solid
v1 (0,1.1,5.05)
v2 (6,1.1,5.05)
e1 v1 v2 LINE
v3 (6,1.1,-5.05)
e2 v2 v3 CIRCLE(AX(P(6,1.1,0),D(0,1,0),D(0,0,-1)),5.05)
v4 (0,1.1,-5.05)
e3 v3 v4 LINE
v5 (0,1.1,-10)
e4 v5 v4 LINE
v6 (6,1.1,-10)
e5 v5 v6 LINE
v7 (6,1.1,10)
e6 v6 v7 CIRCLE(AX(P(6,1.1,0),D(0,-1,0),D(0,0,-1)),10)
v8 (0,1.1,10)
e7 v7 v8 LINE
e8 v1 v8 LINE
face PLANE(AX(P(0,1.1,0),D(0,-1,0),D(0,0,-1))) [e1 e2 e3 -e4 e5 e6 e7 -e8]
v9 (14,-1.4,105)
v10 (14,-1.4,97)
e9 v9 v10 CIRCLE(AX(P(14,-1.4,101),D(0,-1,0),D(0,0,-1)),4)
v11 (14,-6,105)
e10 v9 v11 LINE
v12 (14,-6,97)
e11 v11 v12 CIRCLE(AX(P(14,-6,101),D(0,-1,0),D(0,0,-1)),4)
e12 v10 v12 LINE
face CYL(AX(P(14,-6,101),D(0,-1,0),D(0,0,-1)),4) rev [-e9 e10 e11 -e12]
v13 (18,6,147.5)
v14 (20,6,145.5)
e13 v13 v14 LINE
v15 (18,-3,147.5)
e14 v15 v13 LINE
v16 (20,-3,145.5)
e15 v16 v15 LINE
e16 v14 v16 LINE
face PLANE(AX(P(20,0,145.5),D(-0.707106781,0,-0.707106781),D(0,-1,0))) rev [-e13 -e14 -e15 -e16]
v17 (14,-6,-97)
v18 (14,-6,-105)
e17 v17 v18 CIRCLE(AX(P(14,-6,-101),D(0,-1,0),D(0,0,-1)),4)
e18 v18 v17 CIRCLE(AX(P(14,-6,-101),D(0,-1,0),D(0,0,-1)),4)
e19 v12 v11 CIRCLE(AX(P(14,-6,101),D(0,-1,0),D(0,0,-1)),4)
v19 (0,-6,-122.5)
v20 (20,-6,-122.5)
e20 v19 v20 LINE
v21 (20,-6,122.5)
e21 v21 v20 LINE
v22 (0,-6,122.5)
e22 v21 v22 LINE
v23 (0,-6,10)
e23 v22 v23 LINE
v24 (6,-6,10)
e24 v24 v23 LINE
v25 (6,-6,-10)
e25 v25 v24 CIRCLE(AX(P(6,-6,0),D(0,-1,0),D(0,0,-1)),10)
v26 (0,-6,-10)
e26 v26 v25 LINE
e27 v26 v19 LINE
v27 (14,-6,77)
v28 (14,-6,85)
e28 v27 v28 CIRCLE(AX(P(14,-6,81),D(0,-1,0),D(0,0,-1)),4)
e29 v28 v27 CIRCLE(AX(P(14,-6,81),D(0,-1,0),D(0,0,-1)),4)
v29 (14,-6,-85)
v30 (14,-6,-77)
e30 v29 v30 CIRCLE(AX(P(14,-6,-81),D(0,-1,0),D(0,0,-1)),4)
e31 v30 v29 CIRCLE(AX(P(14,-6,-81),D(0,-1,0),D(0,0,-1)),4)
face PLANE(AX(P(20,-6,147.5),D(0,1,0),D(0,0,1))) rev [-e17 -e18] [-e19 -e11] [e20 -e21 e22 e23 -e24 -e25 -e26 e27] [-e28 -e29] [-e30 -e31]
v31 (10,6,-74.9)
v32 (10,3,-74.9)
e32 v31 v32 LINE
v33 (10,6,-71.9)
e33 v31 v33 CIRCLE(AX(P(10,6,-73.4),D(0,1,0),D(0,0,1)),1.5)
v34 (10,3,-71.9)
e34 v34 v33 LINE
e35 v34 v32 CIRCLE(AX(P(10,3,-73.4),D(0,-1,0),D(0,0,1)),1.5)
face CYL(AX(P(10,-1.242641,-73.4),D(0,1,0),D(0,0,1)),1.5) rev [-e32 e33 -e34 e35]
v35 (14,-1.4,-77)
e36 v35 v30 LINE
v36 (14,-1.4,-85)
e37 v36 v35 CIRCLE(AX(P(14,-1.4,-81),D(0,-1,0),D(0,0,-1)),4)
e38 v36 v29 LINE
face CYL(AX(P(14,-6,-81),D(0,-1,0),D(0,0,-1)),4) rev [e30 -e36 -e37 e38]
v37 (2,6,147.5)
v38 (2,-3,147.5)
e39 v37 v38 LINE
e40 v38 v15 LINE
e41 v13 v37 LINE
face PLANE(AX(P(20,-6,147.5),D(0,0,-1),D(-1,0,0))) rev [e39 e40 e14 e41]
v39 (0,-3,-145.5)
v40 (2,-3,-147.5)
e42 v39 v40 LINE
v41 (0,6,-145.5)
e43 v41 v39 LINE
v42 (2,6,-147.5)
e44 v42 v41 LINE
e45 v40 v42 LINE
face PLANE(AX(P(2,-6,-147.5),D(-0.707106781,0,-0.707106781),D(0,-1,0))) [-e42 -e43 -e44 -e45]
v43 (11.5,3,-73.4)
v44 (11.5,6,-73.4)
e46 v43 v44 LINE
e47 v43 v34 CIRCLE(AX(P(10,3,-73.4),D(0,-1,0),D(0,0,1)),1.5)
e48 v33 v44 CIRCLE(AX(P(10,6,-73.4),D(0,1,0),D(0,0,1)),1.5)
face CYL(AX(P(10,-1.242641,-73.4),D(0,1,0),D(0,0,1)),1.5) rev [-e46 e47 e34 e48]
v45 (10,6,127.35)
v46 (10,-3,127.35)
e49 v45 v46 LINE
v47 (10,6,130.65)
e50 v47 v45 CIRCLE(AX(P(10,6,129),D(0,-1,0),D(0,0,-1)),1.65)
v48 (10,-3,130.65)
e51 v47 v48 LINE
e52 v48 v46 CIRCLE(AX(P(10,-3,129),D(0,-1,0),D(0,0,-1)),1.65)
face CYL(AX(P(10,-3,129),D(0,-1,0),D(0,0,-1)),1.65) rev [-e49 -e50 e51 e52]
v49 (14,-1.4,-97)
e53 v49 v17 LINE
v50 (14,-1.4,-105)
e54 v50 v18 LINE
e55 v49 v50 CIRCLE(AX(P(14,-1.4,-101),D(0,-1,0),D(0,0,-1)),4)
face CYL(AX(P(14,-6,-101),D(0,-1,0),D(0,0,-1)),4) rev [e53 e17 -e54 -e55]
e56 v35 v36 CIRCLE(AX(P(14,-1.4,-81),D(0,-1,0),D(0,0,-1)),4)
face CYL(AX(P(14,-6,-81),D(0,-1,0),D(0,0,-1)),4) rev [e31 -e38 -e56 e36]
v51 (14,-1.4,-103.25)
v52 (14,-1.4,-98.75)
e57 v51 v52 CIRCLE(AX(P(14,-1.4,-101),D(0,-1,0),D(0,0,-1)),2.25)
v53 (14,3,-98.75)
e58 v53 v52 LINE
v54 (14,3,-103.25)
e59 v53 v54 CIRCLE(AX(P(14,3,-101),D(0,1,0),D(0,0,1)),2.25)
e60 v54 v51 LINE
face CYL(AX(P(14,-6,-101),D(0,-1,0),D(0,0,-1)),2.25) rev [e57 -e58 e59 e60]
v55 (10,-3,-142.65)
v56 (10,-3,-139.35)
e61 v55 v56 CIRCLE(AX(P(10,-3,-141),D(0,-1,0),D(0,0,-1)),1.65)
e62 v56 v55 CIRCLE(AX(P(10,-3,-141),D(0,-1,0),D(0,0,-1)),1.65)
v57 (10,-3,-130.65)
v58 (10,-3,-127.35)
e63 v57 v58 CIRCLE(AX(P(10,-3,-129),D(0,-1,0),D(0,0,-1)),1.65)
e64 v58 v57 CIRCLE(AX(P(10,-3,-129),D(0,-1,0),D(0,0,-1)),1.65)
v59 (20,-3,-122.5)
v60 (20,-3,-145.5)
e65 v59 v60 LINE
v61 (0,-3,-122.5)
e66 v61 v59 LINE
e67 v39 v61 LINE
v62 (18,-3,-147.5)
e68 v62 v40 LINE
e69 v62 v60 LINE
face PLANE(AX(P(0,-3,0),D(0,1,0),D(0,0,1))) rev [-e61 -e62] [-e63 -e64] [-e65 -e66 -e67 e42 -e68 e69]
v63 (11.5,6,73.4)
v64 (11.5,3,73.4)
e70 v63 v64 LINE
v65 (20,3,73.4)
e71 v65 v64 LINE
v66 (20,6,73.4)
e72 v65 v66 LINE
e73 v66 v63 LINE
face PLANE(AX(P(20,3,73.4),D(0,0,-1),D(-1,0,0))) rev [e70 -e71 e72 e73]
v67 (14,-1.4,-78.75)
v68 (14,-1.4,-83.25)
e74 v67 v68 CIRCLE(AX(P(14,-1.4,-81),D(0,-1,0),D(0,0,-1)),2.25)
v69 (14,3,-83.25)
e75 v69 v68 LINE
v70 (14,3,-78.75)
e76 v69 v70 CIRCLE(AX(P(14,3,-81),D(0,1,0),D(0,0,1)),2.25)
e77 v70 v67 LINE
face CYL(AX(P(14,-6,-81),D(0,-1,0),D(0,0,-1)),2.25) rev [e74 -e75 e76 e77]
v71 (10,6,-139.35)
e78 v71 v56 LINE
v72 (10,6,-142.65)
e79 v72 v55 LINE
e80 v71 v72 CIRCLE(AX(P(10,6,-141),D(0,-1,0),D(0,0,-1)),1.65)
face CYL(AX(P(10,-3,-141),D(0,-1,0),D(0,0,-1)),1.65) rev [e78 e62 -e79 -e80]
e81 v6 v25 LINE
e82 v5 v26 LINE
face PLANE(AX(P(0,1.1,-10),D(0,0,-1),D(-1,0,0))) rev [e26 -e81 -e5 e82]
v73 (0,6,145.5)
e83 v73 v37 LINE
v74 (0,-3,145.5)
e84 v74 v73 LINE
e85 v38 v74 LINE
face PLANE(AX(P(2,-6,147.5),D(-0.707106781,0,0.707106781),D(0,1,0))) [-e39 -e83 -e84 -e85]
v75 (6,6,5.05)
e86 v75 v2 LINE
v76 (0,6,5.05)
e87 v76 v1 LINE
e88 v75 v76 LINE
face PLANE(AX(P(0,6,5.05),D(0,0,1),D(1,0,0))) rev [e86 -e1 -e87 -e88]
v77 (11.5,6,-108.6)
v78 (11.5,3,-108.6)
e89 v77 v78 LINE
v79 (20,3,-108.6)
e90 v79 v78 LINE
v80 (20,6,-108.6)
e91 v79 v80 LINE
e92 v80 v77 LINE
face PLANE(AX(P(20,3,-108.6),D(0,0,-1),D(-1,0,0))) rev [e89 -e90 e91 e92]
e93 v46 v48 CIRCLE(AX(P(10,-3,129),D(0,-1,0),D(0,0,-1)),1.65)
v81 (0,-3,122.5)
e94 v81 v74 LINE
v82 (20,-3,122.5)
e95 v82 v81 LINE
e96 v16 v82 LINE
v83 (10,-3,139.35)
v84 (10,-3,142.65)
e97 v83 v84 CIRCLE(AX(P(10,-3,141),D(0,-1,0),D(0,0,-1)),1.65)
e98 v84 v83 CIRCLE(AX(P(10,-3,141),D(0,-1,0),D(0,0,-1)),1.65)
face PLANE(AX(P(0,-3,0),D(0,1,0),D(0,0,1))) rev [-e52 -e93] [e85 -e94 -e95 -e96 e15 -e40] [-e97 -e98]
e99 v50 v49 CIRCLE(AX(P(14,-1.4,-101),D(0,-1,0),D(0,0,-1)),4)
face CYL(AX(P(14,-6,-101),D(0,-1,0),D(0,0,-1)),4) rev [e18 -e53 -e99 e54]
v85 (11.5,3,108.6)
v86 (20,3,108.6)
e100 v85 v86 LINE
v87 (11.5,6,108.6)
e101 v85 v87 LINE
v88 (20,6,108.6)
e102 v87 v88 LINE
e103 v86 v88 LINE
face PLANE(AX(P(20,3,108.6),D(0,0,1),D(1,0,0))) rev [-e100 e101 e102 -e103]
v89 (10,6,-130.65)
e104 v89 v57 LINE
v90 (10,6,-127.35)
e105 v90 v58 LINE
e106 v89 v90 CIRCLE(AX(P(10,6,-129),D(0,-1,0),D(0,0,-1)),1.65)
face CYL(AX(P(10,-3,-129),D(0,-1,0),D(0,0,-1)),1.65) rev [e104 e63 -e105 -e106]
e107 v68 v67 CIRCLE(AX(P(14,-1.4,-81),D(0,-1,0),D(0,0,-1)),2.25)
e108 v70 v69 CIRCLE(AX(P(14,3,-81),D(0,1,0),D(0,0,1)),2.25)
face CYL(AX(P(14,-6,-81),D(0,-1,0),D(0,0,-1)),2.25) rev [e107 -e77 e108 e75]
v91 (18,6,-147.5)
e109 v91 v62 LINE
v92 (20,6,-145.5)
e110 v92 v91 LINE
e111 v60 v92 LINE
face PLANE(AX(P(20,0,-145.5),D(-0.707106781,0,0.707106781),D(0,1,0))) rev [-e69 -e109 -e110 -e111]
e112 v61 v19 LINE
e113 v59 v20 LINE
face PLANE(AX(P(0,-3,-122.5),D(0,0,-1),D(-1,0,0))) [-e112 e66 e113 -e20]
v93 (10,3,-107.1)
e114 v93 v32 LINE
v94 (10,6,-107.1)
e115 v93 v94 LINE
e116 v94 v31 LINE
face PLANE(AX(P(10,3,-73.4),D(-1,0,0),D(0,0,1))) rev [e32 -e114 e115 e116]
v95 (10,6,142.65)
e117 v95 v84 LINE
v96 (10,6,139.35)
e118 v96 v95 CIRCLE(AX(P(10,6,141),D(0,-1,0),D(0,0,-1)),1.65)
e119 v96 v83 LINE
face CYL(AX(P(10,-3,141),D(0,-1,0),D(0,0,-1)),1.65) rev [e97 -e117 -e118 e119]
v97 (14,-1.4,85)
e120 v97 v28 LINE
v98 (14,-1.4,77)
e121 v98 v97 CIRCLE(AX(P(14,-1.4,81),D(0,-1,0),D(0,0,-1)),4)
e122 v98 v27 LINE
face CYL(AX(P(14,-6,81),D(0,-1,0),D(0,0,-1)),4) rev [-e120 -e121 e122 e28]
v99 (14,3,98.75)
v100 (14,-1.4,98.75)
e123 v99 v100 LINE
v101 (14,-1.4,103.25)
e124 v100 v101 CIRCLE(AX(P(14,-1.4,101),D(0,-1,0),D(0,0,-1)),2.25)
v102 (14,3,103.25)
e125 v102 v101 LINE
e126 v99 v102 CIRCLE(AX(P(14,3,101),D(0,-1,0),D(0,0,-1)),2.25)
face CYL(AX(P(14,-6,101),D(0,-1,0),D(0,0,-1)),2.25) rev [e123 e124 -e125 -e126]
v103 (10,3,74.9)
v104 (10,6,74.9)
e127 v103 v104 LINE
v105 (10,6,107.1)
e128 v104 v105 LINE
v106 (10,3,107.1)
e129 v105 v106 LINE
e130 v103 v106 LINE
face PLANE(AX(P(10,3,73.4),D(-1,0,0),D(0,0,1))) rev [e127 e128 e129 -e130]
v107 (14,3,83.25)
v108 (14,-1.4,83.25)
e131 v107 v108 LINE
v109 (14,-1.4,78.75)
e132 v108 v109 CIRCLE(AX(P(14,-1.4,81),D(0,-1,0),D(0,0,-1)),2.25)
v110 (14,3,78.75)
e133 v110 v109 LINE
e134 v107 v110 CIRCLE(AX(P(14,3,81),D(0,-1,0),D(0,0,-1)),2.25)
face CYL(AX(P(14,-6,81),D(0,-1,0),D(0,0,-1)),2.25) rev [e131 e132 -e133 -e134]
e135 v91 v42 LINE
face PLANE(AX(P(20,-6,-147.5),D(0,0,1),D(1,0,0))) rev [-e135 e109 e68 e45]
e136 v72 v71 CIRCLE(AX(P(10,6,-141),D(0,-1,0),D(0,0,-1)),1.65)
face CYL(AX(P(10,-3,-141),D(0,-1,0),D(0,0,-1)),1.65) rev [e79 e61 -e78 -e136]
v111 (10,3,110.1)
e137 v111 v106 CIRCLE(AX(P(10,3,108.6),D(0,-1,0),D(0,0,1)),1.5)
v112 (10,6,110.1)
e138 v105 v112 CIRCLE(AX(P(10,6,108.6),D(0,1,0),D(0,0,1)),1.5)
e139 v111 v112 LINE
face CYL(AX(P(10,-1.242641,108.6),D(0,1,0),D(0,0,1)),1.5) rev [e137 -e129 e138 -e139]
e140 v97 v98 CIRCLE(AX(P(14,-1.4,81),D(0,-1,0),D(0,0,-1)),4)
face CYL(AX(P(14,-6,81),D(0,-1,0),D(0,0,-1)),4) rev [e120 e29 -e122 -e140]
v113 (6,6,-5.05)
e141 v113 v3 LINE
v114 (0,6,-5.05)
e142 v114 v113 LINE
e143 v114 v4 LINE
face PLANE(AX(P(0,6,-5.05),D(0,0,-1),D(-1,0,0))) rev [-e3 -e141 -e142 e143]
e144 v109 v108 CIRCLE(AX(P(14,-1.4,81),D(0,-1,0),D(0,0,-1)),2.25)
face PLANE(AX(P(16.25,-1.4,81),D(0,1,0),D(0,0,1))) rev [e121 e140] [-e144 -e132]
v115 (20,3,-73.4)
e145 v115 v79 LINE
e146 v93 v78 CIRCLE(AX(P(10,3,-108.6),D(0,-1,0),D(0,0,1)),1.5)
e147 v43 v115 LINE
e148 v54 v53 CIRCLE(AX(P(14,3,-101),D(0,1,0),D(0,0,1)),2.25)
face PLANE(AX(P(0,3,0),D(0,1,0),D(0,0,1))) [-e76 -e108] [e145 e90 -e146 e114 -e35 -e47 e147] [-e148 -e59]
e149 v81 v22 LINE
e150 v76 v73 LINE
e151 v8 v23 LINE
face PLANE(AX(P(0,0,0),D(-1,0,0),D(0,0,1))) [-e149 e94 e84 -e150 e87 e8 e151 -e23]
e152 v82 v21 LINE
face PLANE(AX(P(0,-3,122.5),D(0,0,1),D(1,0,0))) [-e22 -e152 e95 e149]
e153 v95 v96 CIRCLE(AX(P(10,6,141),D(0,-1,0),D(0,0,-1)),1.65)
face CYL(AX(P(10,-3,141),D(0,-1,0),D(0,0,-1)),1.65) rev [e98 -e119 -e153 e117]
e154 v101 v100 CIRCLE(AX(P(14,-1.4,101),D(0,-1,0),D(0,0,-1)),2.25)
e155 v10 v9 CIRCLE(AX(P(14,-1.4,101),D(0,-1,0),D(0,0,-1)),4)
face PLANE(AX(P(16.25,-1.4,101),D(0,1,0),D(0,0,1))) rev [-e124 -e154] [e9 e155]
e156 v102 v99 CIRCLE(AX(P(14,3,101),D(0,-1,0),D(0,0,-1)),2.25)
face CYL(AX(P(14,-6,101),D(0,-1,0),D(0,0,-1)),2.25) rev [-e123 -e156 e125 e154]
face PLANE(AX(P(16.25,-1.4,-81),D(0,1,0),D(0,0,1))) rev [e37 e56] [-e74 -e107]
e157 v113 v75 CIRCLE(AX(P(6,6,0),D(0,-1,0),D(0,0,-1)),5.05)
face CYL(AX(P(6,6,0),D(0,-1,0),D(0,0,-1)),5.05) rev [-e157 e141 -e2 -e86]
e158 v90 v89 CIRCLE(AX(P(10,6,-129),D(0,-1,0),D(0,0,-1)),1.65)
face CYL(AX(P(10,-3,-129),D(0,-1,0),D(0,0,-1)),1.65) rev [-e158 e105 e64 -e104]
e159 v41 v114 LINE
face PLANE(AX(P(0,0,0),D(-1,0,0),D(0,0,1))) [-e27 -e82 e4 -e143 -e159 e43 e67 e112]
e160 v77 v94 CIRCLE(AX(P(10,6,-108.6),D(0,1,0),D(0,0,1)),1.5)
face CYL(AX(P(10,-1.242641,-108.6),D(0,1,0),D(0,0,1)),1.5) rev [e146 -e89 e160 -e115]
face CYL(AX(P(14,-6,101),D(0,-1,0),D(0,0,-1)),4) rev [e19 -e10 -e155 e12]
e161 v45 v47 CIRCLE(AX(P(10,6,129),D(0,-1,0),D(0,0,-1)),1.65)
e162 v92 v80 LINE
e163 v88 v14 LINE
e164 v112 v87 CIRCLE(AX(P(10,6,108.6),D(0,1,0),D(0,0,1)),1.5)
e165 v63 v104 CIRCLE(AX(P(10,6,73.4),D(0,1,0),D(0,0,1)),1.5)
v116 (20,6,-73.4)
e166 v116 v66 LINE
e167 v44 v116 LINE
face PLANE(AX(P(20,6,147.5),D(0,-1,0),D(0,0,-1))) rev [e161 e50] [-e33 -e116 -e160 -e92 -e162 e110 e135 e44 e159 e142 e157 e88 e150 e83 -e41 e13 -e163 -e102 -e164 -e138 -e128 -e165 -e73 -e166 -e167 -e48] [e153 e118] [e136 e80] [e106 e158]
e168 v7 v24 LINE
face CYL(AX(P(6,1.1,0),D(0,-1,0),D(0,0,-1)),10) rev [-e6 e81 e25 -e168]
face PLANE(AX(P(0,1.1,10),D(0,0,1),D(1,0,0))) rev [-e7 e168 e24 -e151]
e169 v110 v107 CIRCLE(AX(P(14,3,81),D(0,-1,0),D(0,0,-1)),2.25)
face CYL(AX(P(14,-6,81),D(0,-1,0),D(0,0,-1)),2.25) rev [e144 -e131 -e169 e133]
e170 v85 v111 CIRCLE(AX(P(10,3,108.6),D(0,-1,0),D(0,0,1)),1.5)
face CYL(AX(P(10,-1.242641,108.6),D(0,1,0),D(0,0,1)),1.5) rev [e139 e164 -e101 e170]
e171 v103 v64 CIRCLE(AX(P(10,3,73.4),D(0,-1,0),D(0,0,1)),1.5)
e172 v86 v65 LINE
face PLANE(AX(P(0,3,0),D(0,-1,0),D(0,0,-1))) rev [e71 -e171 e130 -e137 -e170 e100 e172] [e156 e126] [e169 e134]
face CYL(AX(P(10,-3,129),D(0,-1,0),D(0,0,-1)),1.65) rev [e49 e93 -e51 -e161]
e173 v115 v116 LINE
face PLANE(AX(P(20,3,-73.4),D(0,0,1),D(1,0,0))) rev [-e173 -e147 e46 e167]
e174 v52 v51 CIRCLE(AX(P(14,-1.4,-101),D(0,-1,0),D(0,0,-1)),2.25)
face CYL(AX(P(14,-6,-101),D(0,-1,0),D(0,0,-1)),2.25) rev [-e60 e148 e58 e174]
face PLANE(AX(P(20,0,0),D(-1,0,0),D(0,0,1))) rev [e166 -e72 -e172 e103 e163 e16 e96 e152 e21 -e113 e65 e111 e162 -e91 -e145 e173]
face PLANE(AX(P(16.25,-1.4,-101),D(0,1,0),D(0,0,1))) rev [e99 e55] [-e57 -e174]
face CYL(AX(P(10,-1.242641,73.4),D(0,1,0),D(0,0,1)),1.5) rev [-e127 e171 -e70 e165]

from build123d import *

# Parameters (mm, degrees)
SKETCH1_W                                            = 295
SKETCH1_H                                            = 12
BOSS_EXTRUDE1_DEPTH                                  = 20
CUT_EXTRUDE1_DEPTH                                   = 150.33268229
CUT_EXTRUDE2_DEPTH                                   = 7.1
SKETCH4_W                                            = 20
SKETCH4_H                                            = 25
CUT_EXTRUDE3_DEPTH                                   = 3
SKETCH5_W                                            = 10
SKETCH5_H                                            = 35.2
CUT_EXTRUDE4_DEPTH                                   = 3
SKETCH7_R                                            = 1.5
CUT_EXTRUDE6_DEPTH                                   = 3
M4_TAPPED_HOLE2_D                                    = 3.3
M4_TAPPED_HOLE2_DEPTH                                = 10.1
M4_TAPPED_HOLE2_TIP                                  = 0.991420021
M4_TAPPED_HOLE1_D                                    = 3.3
M4_TAPPED_HOLE1_DEPTH                                = 10.1
M4_TAPPED_HOLE1_TIP                                  = 0.991420021
CBORE_FOR_M4_HEXAGON_SOCKET_HEAD_CAP_SCR_D           = 4.5
CBORE_FOR_M4_HEXAGON_SOCKET_HEAD_CAP_SCR_CBORE_D     = 8
CBORE_FOR_M4_HEXAGON_SOCKET_HEAD_CAP_SCR_CBORE_DEPTH = 4.6
CHAMFER1_SIZE                                        = 2


with BuildPart() as part:
    # Sketch1 → Boss-Extrude1 (new body)
    with BuildSketch(Plane(origin=(0, 0, 0), x_dir=(0, 0, -1), z_dir=(1, 0, 0))):
        Rectangle(SKETCH1_W, SKETCH1_H)
    extrude(amount=BOSS_EXTRUDE1_DEPTH)

    # Sketch2 → Cut-Extrude1 (cut, through all)
    with BuildSketch(Plane.XZ.offset(6)):
        with BuildLine():
            Line((0, 5.05), (6, 5.05))
            ThreePointArc((6, 5.05), (11.05, 0), (6, -5.05))
            Line((6, -5.05), (0, -5.05))
            ThreePointArc((0, -5.05), (-5.05, 0), (0, 5.05))
        make_face()
    extrude(amount=-CUT_EXTRUDE1_DEPTH, mode=Mode.SUBTRACT)

    # Sketch3 → Cut-Extrude2 (cut)
    with BuildSketch(Plane.XZ.offset(6)):
        with BuildLine():
            Line((0, 10), (6, 10))
            ThreePointArc((6, 10), (16, 0), (6, -10))
            Line((6, -10), (0, -10))
            ThreePointArc((0, -10), (-10, 0), (0, 10))
        make_face()
    extrude(amount=-CUT_EXTRUDE2_DEPTH, mode=Mode.SUBTRACT)

    # Sketch4 → Cut-Extrude3 (cut)
    with BuildSketch(Plane(origin=(0, -6, 0), x_dir=(1, 0, 0), z_dir=(0, 1, 0))):
        with Locations((10, -135)):
            Rectangle(SKETCH4_W, SKETCH4_H)
        with Locations((10, 135)):
            Rectangle(SKETCH4_W, SKETCH4_H)
    extrude(amount=CUT_EXTRUDE3_DEPTH, mode=Mode.SUBTRACT)

    # Sketch5 → Cut-Extrude4 (cut)
    with BuildSketch(Plane(origin=(0, 6, 0), x_dir=(1, 0, 0), z_dir=(0, 1, 0))):
        with Locations((15, 91)):
            Rectangle(SKETCH5_W, SKETCH5_H)
        with Locations((15, -91)):
            Rectangle(SKETCH5_W, SKETCH5_H)
    extrude(amount=-CUT_EXTRUDE4_DEPTH, mode=Mode.SUBTRACT)

    # Sketch7 → Cut-Extrude6 (cut)
    with BuildSketch(Plane(origin=(0, 6, 0), x_dir=(1, 0, 0), z_dir=(0, 1, 0))):
        with Locations((10, 108.6)):
            Circle(SKETCH7_R)
        with Locations((10, 73.4)):
            Circle(SKETCH7_R)
        with Locations((10, -73.4)):
            Circle(SKETCH7_R)
        with Locations((10, -108.6)):
            Circle(SKETCH7_R)
    extrude(amount=-CUT_EXTRUDE6_DEPTH, mode=Mode.SUBTRACT)

    # M4 Tapped Hole2
    with Locations(Plane(origin=(0, -3, 0), x_dir=(-1, 0, 0), z_dir=(0, -1, 0))):
        with Locations((-10, -141), (-10, -129)):
            Hole(M4_TAPPED_HOLE2_D / 2, depth=M4_TAPPED_HOLE2_DEPTH)
            with Locations((0, 0, -(M4_TAPPED_HOLE2_DEPTH + M4_TAPPED_HOLE2_TIP / 2))):  # 118° drill point
                Cone(0, M4_TAPPED_HOLE2_D / 2, M4_TAPPED_HOLE2_TIP, mode=Mode.SUBTRACT)

    # M4 Tapped Hole1
    with Locations(Plane(origin=(0, -3, 0), x_dir=(-1, 0, 0), z_dir=(0, -1, 0))):
        with Locations((-10, 141), (-10, 129)):
            Hole(M4_TAPPED_HOLE1_D / 2, depth=M4_TAPPED_HOLE1_DEPTH)
            with Locations((0, 0, -(M4_TAPPED_HOLE1_DEPTH + M4_TAPPED_HOLE1_TIP / 2))):  # 118° drill point
                Cone(0, M4_TAPPED_HOLE1_D / 2, M4_TAPPED_HOLE1_TIP, mode=Mode.SUBTRACT)

    # CBORE for M4 Hexagon socket head cap screws1 (through all)
    with Locations(Plane(origin=(0, -6, 0), x_dir=(-1, 0, 0), z_dir=(0, -1, 0))):
        with Locations((-14, 101), (-14, 81), (-14, -81), (-14, -101)):
            CounterBoreHole(CBORE_FOR_M4_HEXAGON_SOCKET_HEAD_CAP_SCR_D / 2, CBORE_FOR_M4_HEXAGON_SOCKET_HEAD_CAP_SCR_CBORE_D / 2, CBORE_FOR_M4_HEXAGON_SOCKET_HEAD_CAP_SCR_CBORE_DEPTH)

    # Chamfer1
    chamfer1_edges = [part.edges().sort_by_distance(p)[0] for p in [
        (20, 1.5, 147.5),
        (0, 1.5, 147.5),
        (0, 1.5, -147.5),
        (20, 1.5, -147.5),
    ]]
    chamfer(chamfer1_edges, length=CHAMFER1_SIZE)


solid = part.part
